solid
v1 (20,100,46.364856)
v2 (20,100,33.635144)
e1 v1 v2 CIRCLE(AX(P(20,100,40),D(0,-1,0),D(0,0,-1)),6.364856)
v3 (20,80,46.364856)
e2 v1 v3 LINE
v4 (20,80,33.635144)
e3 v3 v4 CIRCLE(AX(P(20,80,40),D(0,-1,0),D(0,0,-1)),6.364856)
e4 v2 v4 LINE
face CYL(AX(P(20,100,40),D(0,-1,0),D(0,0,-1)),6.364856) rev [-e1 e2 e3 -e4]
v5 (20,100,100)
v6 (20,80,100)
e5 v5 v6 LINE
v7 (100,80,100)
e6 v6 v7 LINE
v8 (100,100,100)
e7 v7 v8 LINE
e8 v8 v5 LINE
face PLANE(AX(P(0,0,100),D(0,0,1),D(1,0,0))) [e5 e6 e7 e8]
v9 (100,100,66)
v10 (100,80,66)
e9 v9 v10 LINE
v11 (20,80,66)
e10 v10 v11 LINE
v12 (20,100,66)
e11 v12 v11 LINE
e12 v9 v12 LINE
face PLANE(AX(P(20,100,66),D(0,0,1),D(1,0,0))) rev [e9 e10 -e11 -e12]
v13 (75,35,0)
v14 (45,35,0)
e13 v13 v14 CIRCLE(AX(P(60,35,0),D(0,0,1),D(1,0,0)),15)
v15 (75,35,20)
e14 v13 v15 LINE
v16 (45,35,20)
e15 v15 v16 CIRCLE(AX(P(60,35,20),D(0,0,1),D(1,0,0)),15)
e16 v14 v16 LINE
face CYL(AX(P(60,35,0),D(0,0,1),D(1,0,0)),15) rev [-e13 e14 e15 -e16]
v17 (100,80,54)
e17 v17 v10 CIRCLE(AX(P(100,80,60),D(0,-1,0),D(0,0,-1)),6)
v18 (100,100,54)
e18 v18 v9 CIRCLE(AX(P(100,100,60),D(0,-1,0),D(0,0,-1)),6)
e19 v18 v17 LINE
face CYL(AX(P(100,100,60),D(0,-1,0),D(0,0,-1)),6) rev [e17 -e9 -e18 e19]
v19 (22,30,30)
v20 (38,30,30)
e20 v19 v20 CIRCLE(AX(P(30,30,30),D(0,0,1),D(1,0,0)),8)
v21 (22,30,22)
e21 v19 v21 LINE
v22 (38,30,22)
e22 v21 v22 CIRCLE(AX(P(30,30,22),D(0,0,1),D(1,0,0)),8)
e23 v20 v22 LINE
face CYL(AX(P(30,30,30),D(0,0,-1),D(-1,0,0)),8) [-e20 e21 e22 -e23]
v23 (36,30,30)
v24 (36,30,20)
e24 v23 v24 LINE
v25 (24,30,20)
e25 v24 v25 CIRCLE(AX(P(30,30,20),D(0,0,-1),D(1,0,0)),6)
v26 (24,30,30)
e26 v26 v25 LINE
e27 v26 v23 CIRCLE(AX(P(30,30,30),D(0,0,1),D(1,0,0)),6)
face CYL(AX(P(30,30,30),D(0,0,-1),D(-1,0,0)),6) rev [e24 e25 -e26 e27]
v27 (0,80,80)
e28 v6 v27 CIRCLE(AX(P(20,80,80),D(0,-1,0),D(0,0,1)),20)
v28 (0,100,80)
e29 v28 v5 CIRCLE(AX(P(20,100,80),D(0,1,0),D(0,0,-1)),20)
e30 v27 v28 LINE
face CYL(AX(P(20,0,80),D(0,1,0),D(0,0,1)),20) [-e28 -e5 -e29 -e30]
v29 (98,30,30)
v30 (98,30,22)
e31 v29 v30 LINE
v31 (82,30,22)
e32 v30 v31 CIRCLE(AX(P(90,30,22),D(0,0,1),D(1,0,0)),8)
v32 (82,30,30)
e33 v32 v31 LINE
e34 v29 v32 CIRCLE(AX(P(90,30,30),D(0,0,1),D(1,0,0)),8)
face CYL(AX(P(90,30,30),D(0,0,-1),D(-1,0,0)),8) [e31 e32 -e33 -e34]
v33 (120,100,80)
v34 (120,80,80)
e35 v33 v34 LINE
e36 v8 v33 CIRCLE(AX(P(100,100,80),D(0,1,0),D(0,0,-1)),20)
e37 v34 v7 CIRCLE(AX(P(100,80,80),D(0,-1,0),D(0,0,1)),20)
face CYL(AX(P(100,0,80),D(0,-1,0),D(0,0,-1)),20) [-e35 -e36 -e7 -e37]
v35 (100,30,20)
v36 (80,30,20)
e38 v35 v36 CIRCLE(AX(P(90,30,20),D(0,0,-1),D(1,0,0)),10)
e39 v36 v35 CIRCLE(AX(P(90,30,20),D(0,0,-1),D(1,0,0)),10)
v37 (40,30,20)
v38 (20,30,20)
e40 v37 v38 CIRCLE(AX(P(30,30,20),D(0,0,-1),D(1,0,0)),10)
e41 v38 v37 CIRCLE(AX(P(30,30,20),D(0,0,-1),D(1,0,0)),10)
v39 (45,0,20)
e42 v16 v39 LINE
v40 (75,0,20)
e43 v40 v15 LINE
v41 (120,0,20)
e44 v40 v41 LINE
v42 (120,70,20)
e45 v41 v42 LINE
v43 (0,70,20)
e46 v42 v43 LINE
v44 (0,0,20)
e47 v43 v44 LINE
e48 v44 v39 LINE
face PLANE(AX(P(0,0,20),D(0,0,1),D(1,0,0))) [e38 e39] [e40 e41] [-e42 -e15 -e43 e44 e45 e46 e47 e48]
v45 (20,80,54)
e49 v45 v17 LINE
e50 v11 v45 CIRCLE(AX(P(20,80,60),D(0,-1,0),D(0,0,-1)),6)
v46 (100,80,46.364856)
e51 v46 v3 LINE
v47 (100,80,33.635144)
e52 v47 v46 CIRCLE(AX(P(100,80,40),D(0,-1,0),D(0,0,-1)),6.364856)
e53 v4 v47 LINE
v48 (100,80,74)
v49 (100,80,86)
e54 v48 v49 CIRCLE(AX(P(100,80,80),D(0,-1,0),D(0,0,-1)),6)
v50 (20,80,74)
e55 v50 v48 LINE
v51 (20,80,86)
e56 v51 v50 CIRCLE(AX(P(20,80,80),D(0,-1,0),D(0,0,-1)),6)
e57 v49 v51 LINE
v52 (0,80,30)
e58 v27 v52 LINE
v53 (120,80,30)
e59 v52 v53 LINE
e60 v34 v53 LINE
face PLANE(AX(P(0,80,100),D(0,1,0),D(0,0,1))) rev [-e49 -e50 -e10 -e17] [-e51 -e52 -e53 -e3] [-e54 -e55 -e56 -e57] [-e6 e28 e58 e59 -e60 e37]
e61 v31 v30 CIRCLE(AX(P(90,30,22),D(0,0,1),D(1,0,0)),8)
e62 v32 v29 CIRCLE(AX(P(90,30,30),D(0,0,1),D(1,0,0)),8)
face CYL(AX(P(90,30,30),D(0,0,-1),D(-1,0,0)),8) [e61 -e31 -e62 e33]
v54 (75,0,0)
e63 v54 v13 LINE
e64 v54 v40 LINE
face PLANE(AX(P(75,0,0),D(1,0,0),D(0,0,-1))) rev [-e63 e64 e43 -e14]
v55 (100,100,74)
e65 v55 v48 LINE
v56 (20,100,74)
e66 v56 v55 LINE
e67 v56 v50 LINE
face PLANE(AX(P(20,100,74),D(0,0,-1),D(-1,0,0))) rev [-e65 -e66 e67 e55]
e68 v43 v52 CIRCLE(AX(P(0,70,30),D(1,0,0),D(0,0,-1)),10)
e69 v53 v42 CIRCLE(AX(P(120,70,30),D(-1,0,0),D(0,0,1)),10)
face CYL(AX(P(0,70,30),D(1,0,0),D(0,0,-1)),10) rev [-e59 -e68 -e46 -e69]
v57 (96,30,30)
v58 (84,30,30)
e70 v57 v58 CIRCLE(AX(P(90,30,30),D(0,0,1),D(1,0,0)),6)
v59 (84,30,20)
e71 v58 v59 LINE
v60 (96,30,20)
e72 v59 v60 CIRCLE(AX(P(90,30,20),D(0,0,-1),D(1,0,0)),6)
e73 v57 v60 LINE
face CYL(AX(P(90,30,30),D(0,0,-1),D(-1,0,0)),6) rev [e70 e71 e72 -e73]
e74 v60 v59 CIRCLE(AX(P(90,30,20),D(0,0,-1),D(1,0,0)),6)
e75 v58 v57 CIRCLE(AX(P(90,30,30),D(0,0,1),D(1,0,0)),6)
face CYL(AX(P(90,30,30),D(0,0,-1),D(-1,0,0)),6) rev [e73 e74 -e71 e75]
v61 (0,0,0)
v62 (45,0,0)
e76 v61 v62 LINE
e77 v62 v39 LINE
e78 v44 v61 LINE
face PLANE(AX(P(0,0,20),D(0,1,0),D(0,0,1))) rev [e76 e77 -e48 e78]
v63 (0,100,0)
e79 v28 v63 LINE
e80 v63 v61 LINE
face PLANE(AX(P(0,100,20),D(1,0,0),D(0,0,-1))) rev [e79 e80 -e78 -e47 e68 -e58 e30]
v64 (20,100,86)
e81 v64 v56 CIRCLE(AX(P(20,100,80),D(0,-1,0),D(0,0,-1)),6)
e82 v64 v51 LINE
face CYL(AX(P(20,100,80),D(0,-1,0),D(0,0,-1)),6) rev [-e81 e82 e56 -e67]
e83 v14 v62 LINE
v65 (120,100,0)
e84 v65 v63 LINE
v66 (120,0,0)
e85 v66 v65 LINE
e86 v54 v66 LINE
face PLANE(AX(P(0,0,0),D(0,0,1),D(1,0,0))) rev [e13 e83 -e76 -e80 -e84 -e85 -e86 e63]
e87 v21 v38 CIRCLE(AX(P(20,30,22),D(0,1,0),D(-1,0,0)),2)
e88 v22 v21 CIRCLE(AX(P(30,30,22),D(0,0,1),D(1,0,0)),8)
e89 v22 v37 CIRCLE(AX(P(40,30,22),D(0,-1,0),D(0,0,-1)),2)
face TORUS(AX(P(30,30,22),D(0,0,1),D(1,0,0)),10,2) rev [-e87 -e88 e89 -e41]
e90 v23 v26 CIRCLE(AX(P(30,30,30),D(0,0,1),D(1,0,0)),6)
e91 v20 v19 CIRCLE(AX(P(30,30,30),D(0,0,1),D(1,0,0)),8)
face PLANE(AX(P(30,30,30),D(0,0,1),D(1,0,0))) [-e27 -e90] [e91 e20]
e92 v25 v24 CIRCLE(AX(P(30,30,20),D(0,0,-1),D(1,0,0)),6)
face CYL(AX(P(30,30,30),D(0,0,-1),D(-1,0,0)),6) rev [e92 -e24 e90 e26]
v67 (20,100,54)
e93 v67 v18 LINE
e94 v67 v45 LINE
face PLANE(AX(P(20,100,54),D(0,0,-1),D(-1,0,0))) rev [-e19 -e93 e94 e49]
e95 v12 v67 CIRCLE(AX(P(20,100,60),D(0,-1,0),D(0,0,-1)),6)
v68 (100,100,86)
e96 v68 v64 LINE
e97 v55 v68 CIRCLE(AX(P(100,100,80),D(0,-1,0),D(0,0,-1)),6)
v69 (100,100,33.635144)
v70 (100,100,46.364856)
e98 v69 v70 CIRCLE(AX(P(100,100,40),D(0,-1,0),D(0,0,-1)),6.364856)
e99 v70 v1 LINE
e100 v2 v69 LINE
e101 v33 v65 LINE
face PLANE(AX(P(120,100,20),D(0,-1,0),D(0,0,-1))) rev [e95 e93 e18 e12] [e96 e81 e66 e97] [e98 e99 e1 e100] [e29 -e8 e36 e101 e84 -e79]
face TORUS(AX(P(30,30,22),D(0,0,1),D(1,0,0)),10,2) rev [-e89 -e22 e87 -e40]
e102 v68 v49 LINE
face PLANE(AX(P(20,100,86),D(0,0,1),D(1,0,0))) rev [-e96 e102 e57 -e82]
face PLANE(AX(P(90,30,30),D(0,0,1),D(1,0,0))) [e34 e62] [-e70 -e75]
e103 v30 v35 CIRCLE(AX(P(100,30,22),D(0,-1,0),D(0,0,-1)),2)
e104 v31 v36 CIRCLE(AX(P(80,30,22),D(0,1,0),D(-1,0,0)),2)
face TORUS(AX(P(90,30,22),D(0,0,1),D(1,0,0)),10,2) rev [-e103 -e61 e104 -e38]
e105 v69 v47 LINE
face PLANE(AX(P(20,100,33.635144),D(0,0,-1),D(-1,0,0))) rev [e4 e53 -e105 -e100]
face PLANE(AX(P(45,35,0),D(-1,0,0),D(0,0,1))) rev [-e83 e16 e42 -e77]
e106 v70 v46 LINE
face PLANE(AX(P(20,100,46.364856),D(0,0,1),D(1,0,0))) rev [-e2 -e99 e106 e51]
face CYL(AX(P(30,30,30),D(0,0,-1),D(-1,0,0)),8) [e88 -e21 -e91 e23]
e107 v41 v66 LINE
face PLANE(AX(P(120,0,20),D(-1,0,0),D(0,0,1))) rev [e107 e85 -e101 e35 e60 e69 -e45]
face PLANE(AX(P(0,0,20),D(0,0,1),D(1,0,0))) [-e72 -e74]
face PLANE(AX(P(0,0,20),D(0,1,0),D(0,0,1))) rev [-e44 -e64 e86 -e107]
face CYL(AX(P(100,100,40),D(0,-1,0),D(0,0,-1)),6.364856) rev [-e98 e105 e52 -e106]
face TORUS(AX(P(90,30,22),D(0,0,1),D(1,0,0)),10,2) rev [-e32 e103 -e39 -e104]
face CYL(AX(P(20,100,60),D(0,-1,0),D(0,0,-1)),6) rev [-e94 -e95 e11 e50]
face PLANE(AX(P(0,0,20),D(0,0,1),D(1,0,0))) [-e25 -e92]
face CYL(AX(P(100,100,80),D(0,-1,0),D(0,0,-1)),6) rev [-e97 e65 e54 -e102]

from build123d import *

# Parameters (mm, degrees)
BACK_PLATE_PROFILE_W        = 120
BACK_PLATE_PROFILE_H        = 100
BACK_PLATE_120X100X20_DEPTH = 20
TOP_ARM_PROFILE_W           = 120
TOP_ARM_PROFILE_H           = 20
TOP_ARM_80_DEPTH            = 80
SLOT_1_CUT_DEPTH            = 176.499287748
SLOT_2_CUT_DEPTH            = 176.499287748
SLOT_3_CUT_DEPTH            = 176.499287748
ARM_ROOT_FILLET_R10_R       = 10
ARM_CORNER_ROUND_R20_R      = 20
BACK_PLATE_CUT_30_DEPTH     = 176.499287748
BOSS_A_SKETCH_R             = 8
BOSS_A_SKETCH_R_2           = 6
MOUNTING_BOSS_A_DEPTH       = 10
BOSS_B_SKETCH_R             = 8
BOSS_B_SKETCH_R_2           = 6
MOUNTING_BOSS_B_DEPTH       = 10
BOSS_EDGE_FILLET_R2_R       = 2


with BuildPart() as part:
    # Back Plate Profile → Back Plate 120x100x20 (new body)
    with BuildSketch(Plane.XY):
        with Locations((60, 50)):
            Rectangle(BACK_PLATE_PROFILE_W, BACK_PLATE_PROFILE_H)
    extrude(amount=BACK_PLATE_120X100X20_DEPTH)

    # Top Arm Profile → Top Arm 80 (add)
    with BuildSketch(Plane.XY.offset(20)):
        with Locations((60, 90)):
            Rectangle(TOP_ARM_PROFILE_W, TOP_ARM_PROFILE_H)
    extrude(amount=TOP_ARM_80_DEPTH)

    # Slot 1 Sketch → Slot 1 Cut (cut, through all)
    with BuildSketch(Plane.XZ.offset(-80)):
        with BuildLine():
            Line((20, 86), (100, 86))
            ThreePointArc((100, 86), (106, 80), (100, 74))
            Line((100, 74), (20, 74))
            ThreePointArc((20, 74), (14, 80), (20, 86))
        make_face()
    extrude(amount=-SLOT_1_CUT_DEPTH, mode=Mode.SUBTRACT)

    # Slot 2 Sketch → Slot 2 Cut (cut, through all)
    with BuildSketch(Plane.XZ.offset(-80)):
        with BuildLine():
            Line((20, 66), (100, 66))
            ThreePointArc((100, 66), (106, 60), (100, 54))
            Line((100, 54), (20, 54))
            ThreePointArc((20, 54), (14, 60), (20, 66))
        make_face()
    extrude(amount=-SLOT_2_CUT_DEPTH, mode=Mode.SUBTRACT)

    # Slot 3 Sketch → Slot 3 Cut (cut, through all)
    with BuildSketch(Plane.XZ.offset(-80)):
        with BuildLine():
            Line((20, 46.364855501), (100, 46.364855501))
            ThreePointArc((100, 46.364855501), (106.364855501, 40), (100, 33.635144499))
            Line((100, 33.635144499), (20, 33.635144499))
            ThreePointArc((20, 33.635144499), (13.635144499, 40), (20, 46.364855501))
        make_face()
    extrude(amount=-SLOT_3_CUT_DEPTH, mode=Mode.SUBTRACT)

    # Arm Root Fillet R10
    arm_root_fillet_r10_edges = [part.edges().sort_by_distance(p)[0] for p in [
        (60, 80, 20),
    ]]
    fillet(arm_root_fillet_r10_edges, radius=ARM_ROOT_FILLET_R10_R)

    # Arm Corner Round R20
    arm_corner_round_r20_edges = [part.edges().sort_by_distance(p)[0] for p in [
        (0, 90, 100),
        (120, 90, 100),
    ]]
    fillet(arm_corner_round_r20_edges, radius=ARM_CORNER_ROUND_R20_R)

    # Back Plate Cut Sketch → Back Plate Cut 30 (cut, through all)
    with BuildSketch(Plane.XY.offset(20)):
        with BuildLine():
            Line((45, 35), (45, 0))
            Line((45, 0), (75, 0))
            Line((75, 0), (75, 35))
            ThreePointArc((75, 35), (60, 50), (45, 35))
        make_face()
    extrude(amount=-BACK_PLATE_CUT_30_DEPTH, mode=Mode.SUBTRACT)

    # Boss A Sketch → Mounting Boss A (add)
    with BuildSketch(Plane.XY.offset(20)):
        with Locations((30, 30)):
            Circle(BOSS_A_SKETCH_R)
        with Locations((30, 30)):
            Circle(BOSS_A_SKETCH_R_2, mode=Mode.SUBTRACT)
    extrude(amount=MOUNTING_BOSS_A_DEPTH)

    # Boss B Sketch → Mounting Boss B (add)
    with BuildSketch(Plane.XY.offset(20)):
        with Locations((90, 30)):
            Circle(BOSS_B_SKETCH_R)
        with Locations((90, 30)):
            Circle(BOSS_B_SKETCH_R_2, mode=Mode.SUBTRACT)
    extrude(amount=MOUNTING_BOSS_B_DEPTH)

    # Boss Edge Fillet R2
    boss_edge_fillet_r2_edges = [part.edges().sort_by_distance(p)[0] for p in [
        (22, 30, 20),
        (82, 30, 20),
    ]]
    fillet(boss_edge_fillet_r2_edges, radius=BOSS_EDGE_FILLET_R2_R)


solid = part.part
